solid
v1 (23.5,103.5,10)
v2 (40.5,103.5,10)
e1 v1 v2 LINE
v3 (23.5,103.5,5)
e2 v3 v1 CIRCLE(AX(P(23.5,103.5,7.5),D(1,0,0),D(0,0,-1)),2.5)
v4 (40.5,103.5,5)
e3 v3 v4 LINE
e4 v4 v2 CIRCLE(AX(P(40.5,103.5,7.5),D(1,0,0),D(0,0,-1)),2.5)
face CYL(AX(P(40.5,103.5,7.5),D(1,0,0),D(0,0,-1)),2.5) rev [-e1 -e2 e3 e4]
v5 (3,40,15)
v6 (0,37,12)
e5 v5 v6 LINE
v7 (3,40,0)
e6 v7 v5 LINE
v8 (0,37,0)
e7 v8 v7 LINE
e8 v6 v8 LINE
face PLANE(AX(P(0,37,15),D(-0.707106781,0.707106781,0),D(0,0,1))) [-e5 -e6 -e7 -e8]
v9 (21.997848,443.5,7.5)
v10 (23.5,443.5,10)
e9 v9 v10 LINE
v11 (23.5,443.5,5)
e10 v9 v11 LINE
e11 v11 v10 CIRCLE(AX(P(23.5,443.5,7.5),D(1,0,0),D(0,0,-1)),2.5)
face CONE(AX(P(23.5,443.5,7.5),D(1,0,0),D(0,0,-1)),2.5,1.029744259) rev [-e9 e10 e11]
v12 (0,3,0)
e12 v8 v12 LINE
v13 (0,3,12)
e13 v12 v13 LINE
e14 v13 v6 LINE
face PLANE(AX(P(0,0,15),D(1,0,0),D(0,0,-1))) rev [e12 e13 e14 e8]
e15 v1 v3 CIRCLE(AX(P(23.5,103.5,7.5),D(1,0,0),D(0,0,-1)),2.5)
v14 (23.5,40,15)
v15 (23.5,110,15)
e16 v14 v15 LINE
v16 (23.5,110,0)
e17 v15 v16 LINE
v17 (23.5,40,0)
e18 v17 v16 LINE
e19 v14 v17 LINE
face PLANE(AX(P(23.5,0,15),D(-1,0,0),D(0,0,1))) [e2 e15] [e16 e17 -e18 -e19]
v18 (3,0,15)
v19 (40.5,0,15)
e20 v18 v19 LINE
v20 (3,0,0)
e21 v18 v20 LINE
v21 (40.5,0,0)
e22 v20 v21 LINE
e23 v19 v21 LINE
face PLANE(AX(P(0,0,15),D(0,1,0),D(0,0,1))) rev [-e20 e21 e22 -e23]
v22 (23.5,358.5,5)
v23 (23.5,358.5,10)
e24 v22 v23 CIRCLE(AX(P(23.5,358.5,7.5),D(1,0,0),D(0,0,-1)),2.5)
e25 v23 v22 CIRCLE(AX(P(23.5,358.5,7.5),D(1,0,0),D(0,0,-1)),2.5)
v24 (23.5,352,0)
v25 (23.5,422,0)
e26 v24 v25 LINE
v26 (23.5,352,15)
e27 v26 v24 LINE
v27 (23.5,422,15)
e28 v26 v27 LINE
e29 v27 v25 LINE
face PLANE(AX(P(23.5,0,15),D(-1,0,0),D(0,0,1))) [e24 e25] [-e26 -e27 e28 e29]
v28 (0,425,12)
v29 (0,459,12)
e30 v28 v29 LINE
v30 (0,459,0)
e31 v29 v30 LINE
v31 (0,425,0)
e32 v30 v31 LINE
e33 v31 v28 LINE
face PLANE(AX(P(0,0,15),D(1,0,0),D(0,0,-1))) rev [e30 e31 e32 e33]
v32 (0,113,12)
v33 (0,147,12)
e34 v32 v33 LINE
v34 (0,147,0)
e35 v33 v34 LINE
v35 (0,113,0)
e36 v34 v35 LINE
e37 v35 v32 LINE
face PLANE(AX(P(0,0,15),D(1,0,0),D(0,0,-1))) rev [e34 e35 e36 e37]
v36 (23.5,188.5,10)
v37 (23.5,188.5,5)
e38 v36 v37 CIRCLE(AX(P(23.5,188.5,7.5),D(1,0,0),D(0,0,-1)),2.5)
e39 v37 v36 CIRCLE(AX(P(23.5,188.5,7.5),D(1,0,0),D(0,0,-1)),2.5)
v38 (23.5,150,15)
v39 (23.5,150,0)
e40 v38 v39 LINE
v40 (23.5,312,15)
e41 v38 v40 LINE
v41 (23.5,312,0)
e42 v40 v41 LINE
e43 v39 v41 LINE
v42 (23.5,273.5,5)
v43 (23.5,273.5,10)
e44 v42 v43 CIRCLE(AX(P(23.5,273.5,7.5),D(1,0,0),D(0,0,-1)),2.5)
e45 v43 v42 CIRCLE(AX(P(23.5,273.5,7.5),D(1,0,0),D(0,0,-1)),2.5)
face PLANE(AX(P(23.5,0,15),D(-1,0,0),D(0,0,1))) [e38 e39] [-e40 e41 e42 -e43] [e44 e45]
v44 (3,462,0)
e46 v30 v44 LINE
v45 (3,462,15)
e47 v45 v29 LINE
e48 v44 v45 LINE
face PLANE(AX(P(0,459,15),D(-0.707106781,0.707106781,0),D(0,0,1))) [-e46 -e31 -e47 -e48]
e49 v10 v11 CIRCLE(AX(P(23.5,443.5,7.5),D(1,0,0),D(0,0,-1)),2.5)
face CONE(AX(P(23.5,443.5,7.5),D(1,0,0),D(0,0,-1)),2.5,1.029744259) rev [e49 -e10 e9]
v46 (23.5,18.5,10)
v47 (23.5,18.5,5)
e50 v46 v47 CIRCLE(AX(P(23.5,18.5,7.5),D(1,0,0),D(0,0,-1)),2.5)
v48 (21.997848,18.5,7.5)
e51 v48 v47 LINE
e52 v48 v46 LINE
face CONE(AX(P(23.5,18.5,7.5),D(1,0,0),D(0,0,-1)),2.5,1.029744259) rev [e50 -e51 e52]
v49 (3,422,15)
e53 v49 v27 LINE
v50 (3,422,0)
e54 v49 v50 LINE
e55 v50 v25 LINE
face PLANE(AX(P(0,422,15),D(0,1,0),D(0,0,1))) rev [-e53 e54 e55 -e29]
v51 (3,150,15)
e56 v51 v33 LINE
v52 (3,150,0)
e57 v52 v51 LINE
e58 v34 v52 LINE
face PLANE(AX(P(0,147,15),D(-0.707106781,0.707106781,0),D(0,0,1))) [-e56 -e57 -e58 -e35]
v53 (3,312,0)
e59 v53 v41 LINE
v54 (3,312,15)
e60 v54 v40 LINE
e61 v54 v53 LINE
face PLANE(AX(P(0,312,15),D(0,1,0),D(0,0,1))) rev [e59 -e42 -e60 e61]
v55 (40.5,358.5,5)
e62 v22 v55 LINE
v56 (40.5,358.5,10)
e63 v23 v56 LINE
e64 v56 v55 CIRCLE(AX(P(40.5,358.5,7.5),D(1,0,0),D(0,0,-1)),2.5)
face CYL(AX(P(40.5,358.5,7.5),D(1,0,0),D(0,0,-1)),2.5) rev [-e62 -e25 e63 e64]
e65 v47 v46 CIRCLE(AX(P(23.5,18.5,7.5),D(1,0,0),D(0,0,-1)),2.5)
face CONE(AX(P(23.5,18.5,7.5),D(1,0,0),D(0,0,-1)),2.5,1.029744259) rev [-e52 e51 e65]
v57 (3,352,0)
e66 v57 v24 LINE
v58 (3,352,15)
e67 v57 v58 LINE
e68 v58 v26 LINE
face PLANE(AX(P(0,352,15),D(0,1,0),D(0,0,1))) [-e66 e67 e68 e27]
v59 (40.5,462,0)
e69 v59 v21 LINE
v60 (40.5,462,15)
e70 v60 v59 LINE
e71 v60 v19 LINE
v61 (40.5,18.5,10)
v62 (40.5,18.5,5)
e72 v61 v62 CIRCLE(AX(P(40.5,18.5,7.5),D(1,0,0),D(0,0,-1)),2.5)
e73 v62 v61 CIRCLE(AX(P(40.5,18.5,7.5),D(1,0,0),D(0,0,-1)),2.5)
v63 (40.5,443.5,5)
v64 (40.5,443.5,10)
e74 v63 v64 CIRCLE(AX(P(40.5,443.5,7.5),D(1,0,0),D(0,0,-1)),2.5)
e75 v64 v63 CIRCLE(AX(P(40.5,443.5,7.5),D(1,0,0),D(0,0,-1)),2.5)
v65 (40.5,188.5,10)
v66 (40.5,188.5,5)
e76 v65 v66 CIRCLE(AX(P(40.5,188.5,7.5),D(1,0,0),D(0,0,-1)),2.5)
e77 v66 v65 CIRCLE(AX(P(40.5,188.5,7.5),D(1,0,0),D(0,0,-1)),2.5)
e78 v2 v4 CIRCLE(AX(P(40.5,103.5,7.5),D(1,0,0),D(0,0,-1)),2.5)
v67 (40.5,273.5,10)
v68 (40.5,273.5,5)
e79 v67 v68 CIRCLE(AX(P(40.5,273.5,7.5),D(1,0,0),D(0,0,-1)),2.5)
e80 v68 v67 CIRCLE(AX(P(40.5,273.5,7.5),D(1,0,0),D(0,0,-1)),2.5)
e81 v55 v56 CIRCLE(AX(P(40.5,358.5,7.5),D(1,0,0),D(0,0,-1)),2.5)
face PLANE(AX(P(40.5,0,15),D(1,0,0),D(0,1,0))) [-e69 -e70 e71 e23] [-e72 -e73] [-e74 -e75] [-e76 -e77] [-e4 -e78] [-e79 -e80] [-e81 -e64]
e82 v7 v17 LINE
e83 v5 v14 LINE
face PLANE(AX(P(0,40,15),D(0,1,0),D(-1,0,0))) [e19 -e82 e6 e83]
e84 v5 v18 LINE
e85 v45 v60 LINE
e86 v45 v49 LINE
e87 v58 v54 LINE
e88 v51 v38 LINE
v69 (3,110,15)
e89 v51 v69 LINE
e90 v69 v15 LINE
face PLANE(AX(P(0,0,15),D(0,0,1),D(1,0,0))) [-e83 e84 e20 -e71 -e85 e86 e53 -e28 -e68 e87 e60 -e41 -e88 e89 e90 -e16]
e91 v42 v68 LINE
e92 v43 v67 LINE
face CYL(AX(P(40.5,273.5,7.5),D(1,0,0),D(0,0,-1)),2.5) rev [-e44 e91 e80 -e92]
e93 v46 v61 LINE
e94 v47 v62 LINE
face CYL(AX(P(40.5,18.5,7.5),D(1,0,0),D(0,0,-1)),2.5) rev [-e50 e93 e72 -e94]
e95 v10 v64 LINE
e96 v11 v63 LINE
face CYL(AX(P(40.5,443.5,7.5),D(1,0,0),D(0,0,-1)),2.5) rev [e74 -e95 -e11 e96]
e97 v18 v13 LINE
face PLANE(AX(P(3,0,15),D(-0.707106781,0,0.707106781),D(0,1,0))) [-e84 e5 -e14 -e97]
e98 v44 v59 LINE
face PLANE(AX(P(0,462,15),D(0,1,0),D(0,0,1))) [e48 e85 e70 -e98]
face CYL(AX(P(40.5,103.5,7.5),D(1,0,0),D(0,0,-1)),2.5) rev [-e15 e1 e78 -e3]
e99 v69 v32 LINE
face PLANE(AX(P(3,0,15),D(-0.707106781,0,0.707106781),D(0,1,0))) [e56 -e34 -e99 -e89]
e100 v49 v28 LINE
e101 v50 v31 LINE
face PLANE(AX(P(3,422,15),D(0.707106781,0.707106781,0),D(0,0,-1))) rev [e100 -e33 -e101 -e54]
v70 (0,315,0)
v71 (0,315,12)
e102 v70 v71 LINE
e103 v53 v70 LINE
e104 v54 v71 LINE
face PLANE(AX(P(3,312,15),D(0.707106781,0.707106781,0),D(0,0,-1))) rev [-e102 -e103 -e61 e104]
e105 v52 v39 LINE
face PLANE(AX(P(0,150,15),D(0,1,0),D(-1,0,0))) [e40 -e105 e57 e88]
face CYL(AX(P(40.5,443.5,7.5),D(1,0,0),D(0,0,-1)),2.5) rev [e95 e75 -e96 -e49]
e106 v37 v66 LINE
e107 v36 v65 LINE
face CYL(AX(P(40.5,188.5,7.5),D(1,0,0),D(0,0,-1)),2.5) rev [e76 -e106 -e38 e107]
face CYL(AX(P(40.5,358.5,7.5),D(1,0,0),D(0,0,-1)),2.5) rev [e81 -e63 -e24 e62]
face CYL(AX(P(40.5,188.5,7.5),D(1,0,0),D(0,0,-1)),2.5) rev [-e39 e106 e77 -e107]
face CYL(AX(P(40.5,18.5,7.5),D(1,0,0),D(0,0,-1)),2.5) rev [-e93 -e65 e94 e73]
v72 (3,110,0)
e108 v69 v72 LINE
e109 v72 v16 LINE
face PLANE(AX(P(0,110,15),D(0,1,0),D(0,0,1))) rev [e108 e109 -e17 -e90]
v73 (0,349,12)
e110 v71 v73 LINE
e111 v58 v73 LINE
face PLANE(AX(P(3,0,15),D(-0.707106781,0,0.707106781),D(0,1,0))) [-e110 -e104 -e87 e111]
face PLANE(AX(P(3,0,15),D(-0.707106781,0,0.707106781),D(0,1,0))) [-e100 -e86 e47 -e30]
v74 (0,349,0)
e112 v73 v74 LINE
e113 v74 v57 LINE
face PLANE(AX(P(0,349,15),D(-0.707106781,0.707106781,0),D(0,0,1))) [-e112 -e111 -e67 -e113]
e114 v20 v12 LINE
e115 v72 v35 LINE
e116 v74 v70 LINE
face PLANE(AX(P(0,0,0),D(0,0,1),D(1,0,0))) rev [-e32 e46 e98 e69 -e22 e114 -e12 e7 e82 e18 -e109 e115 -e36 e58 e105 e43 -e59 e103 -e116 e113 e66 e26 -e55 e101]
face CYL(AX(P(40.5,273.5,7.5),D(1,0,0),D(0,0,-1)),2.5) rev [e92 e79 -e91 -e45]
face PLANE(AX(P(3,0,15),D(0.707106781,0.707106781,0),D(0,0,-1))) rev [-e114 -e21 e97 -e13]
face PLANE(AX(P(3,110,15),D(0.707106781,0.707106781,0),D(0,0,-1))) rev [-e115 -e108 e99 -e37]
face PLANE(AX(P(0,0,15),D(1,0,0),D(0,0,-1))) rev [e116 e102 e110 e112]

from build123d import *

# Parameters (mm, degrees)
EXTRUDE_1_DEPTH        = 15
CHAMFER_1_SIZE         = 3
HOLE_WIZARD_M6_1_D     = 5
HOLE_WIZARD_M6_1_DEPTH = 17
HOLE_WIZARD_M6_1_TIP   = 1.502151548


with BuildPart() as part:
    # 草图1 → 凸台-拉伸1 (new body)
    with BuildSketch(Plane.XY):
        Polygon((0, 462), (0, 422), (23.5, 422), (23.5, 352), (0, 352), (0, 312), (23.5, 312), (23.5, 150), (0, 150), (0, 110), (23.5, 110), (23.5, 40), (0, 40), (0, 0), (40.5, 0), (40.5, 462), align=None)
    extrude(amount=EXTRUDE_1_DEPTH)

    # 倒角1
    chamfer_1_edges = [part.edges().sort_by_distance(p)[0] for p in [
        (0, 20, 15),
        (0, 110, 7.5),
        (0, 150, 7.5),
        (0, 312, 7.5),
        (0, 352, 7.5),
        (0, 422, 7.5),
        (0, 462, 7.5),
        (0, 0, 7.5),
        (0, 40, 7.5),
        (0, 442, 15),
        (0, 332, 15),
        (0, 130, 15),
    ]]
    chamfer(chamfer_1_edges, length=CHAMFER_1_SIZE)

    # M6 螺纹孔1
    with Locations(Plane(origin=(40.5, 0, 0), x_dir=(0, 0, -1), z_dir=(1, 0, 0))):
        with Locations((-7.5, 443.5), (-7.5, 358.5), (-7.5, 273.5), (-7.5, 188.5), (-7.5, 103.5), (-7.5, 18.5)):
            Hole(HOLE_WIZARD_M6_1_D / 2, depth=HOLE_WIZARD_M6_1_DEPTH)
            with Locations((0, 0, -(HOLE_WIZARD_M6_1_DEPTH + HOLE_WIZARD_M6_1_TIP / 2))):  # 118° drill point
                Cone(0, HOLE_WIZARD_M6_1_D / 2, HOLE_WIZARD_M6_1_TIP, mode=Mode.SUBTRACT)


solid = part.part
